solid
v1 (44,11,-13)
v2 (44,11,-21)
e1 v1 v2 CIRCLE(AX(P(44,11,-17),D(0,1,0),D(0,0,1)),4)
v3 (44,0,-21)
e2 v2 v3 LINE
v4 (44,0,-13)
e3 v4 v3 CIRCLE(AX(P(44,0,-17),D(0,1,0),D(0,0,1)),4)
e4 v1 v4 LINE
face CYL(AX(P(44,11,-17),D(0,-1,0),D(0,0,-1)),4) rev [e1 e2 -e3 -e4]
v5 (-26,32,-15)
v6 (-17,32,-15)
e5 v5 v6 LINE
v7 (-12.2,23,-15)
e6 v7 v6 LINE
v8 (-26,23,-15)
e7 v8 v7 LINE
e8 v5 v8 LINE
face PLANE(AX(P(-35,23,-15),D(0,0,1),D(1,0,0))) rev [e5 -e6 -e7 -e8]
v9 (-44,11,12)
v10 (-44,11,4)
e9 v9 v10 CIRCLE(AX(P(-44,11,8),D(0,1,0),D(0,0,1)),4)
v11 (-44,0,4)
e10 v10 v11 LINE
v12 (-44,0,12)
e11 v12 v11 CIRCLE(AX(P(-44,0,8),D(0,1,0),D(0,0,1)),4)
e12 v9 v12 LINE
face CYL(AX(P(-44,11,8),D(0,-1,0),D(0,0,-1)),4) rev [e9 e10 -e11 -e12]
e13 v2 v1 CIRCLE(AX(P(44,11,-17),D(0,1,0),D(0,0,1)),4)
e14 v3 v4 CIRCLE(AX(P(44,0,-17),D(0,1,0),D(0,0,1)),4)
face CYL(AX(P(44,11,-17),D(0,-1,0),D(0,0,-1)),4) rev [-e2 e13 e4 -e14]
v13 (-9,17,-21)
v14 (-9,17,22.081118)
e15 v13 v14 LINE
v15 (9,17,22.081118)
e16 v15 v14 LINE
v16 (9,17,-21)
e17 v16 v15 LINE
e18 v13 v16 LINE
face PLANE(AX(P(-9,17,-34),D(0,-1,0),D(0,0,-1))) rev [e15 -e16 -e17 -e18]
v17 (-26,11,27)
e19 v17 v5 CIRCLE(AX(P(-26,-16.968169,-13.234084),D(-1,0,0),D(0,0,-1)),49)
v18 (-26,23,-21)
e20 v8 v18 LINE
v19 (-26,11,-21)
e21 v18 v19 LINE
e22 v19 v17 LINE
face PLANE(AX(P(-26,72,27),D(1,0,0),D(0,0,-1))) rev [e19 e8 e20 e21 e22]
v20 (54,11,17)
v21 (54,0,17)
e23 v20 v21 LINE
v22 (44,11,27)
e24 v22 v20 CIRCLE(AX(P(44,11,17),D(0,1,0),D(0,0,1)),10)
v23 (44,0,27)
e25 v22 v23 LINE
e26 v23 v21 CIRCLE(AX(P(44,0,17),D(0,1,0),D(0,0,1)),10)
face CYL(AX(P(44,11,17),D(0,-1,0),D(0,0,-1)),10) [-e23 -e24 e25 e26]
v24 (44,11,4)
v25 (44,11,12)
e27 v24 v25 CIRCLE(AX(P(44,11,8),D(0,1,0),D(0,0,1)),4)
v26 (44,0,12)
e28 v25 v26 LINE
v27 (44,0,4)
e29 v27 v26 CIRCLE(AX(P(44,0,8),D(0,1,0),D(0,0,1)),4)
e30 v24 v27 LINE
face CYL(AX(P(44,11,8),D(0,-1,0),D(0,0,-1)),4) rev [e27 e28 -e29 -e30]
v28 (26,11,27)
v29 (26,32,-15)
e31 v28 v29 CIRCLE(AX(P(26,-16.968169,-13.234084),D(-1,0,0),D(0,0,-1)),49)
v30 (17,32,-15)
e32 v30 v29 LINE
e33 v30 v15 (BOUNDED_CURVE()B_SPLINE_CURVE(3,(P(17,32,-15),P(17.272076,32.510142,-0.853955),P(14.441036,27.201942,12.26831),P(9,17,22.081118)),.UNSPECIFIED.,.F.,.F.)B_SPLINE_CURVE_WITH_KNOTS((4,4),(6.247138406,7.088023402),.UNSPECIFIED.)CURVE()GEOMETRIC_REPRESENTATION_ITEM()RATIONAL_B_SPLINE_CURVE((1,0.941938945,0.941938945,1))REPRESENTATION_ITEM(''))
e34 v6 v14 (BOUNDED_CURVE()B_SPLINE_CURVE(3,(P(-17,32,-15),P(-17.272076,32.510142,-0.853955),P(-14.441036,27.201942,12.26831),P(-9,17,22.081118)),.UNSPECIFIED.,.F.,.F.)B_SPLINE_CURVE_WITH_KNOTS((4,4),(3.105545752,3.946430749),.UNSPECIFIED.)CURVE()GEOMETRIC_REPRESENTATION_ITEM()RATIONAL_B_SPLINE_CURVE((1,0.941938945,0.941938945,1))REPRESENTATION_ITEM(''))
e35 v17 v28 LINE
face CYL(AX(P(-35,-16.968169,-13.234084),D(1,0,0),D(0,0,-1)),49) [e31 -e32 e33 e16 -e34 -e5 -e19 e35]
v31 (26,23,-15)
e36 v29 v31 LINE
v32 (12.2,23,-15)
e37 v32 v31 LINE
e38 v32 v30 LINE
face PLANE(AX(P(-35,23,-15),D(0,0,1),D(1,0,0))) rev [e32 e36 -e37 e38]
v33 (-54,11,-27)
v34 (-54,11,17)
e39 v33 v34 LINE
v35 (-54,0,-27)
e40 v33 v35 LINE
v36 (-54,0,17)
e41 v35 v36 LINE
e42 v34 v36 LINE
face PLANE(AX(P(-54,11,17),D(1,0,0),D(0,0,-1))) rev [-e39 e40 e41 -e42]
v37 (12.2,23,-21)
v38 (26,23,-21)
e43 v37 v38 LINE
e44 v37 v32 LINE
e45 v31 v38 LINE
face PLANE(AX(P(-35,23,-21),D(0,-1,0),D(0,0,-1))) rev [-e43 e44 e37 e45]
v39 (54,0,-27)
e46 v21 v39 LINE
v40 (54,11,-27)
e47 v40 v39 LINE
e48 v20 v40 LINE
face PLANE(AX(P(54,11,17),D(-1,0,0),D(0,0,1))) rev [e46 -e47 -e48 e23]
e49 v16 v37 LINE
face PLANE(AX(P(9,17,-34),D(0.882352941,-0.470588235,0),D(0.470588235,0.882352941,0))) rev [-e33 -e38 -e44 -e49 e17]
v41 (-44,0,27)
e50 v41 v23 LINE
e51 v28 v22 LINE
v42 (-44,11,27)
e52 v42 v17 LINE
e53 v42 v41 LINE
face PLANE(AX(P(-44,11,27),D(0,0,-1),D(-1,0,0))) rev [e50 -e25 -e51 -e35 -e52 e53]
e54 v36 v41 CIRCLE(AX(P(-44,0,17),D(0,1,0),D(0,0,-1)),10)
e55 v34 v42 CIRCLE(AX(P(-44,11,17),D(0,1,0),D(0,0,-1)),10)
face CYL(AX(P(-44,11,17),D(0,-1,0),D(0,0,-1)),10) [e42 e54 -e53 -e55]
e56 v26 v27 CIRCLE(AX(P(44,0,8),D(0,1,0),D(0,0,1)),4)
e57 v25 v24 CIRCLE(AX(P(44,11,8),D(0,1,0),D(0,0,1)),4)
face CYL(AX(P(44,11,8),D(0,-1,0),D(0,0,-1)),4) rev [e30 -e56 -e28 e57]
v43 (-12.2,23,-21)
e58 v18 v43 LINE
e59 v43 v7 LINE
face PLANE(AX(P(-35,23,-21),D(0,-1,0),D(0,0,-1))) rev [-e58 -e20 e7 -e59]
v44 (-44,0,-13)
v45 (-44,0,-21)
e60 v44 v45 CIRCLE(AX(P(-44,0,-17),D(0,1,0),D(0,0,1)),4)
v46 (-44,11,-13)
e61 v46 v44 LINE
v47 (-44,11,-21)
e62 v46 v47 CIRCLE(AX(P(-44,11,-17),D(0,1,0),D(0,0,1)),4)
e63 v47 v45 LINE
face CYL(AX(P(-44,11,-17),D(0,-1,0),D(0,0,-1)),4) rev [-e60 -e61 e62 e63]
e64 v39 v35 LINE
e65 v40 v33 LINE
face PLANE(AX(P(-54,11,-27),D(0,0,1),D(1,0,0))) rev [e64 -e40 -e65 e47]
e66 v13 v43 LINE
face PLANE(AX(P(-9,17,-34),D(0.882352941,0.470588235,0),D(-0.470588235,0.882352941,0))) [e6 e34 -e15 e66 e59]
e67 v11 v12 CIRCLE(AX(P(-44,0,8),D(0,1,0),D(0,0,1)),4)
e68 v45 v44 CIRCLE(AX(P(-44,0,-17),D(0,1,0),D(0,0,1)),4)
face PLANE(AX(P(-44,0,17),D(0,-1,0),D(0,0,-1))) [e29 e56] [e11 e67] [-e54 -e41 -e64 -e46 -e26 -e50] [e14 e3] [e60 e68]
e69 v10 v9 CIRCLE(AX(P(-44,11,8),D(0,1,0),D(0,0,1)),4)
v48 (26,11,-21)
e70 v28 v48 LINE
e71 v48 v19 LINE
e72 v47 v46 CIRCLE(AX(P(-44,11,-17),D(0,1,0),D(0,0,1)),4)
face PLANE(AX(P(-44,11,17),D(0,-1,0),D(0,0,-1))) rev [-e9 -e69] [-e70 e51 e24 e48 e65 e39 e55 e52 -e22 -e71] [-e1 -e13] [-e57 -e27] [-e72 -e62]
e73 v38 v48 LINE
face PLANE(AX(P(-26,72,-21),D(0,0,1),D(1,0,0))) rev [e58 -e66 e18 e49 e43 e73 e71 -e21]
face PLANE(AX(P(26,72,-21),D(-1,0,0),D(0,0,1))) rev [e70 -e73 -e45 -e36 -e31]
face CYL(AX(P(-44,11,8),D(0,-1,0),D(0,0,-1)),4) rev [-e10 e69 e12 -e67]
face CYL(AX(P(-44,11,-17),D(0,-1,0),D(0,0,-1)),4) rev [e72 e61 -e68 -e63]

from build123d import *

# Parameters (mm, degrees)
BASE_PLATE_SKETCH_R          = 4
BASE_PLATE_DEPTH             = 11
SADDLE_BLOCK_SKETCH_W        = 52
SADDLE_BLOCK_SKETCH_H        = 48
SADDLE_BLOCK_DEPTH           = 61
SADDLE_ARC_PROFILE_CUT_DEPTH = 61
SADDLE_RELIEF_CUT_DEPTH      = 61


with BuildPart() as part:
    # Base Plate Sketch → Base Plate (new body)
    with BuildSketch(Plane(origin=(0, 0, 0), x_dir=(1, 0, 0), z_dir=(0, 1, 0))):
        with BuildLine():
            Line((-44, -27), (44, -27))
            ThreePointArc((44, -27), (51.071067812, -24.071067812), (54, -17))
            Line((54, -17), (54, 27))
            Line((54, 27), (-54, 27))
            Line((-54, 27), (-54, -17))
            ThreePointArc((-54, -17), (-51.071067812, -24.071067812), (-44, -27))
        make_face()
        with Locations(Location((-44, 17, 0), (0, 0, 270))):
            Circle(BASE_PLATE_SKETCH_R, mode=Mode.SUBTRACT)
        with Locations(Location((-44, -8, 0), (0, 0, 270))):
            Circle(BASE_PLATE_SKETCH_R, mode=Mode.SUBTRACT)
        with Locations(Location((44, 17, 0), (0, 0, 270))):
            Circle(BASE_PLATE_SKETCH_R, mode=Mode.SUBTRACT)
        with Locations(Location((44, -8, 0), (0, 0, 270))):
            Circle(BASE_PLATE_SKETCH_R, mode=Mode.SUBTRACT)
    extrude(amount=BASE_PLATE_DEPTH)

    # Saddle Block Sketch → Saddle Block (add)
    with BuildSketch(Plane(origin=(0, 11, 0), x_dir=(1, 0, 0), z_dir=(0, 1, 0))):
        with Locations((0, -3)):
            Rectangle(SADDLE_BLOCK_SKETCH_W, SADDLE_BLOCK_SKETCH_H)
    extrude(amount=SADDLE_BLOCK_DEPTH)

    # Saddle Arc Profile Sketch → Saddle Arc Profile Cut (cut)
    with BuildSketch(Plane(origin=(26, 0, 0), x_dir=(0, 0, -1), z_dir=(1, 0, 0))):
        with BuildLine():
            Line((15, 23), (15, 32))
            ThreePointArc((15, 32), (-8.67938185, 26.8587637), (-27, 11))
            Line((-27, 11), (-38.885663345, 11))
            Line((-38.885663345, 11), (-38.885663345, 85.95954857))
            Line((-38.885663345, 85.95954857), (45.449794115, 85.95954857))
            Line((45.449794115, 85.95954857), (44.243086456, 28.305738224))
            Line((44.243086456, 28.305738224), (21, 23))
            Line((21, 23), (15, 23))
        make_face()
    extrude(amount=-SADDLE_ARC_PROFILE_CUT_DEPTH, mode=Mode.SUBTRACT)

    # Saddle Relief Sketch → Saddle Relief Cut (cut)
    with BuildSketch(Plane.XY.offset(27)):
        Polygon((-17.016976715, 32.031831341), (17.016976715, 32.031831341), (9, 17), (-9, 17), align=None)
    extrude(amount=-SADDLE_RELIEF_CUT_DEPTH, mode=Mode.SUBTRACT)


solid = part.part
